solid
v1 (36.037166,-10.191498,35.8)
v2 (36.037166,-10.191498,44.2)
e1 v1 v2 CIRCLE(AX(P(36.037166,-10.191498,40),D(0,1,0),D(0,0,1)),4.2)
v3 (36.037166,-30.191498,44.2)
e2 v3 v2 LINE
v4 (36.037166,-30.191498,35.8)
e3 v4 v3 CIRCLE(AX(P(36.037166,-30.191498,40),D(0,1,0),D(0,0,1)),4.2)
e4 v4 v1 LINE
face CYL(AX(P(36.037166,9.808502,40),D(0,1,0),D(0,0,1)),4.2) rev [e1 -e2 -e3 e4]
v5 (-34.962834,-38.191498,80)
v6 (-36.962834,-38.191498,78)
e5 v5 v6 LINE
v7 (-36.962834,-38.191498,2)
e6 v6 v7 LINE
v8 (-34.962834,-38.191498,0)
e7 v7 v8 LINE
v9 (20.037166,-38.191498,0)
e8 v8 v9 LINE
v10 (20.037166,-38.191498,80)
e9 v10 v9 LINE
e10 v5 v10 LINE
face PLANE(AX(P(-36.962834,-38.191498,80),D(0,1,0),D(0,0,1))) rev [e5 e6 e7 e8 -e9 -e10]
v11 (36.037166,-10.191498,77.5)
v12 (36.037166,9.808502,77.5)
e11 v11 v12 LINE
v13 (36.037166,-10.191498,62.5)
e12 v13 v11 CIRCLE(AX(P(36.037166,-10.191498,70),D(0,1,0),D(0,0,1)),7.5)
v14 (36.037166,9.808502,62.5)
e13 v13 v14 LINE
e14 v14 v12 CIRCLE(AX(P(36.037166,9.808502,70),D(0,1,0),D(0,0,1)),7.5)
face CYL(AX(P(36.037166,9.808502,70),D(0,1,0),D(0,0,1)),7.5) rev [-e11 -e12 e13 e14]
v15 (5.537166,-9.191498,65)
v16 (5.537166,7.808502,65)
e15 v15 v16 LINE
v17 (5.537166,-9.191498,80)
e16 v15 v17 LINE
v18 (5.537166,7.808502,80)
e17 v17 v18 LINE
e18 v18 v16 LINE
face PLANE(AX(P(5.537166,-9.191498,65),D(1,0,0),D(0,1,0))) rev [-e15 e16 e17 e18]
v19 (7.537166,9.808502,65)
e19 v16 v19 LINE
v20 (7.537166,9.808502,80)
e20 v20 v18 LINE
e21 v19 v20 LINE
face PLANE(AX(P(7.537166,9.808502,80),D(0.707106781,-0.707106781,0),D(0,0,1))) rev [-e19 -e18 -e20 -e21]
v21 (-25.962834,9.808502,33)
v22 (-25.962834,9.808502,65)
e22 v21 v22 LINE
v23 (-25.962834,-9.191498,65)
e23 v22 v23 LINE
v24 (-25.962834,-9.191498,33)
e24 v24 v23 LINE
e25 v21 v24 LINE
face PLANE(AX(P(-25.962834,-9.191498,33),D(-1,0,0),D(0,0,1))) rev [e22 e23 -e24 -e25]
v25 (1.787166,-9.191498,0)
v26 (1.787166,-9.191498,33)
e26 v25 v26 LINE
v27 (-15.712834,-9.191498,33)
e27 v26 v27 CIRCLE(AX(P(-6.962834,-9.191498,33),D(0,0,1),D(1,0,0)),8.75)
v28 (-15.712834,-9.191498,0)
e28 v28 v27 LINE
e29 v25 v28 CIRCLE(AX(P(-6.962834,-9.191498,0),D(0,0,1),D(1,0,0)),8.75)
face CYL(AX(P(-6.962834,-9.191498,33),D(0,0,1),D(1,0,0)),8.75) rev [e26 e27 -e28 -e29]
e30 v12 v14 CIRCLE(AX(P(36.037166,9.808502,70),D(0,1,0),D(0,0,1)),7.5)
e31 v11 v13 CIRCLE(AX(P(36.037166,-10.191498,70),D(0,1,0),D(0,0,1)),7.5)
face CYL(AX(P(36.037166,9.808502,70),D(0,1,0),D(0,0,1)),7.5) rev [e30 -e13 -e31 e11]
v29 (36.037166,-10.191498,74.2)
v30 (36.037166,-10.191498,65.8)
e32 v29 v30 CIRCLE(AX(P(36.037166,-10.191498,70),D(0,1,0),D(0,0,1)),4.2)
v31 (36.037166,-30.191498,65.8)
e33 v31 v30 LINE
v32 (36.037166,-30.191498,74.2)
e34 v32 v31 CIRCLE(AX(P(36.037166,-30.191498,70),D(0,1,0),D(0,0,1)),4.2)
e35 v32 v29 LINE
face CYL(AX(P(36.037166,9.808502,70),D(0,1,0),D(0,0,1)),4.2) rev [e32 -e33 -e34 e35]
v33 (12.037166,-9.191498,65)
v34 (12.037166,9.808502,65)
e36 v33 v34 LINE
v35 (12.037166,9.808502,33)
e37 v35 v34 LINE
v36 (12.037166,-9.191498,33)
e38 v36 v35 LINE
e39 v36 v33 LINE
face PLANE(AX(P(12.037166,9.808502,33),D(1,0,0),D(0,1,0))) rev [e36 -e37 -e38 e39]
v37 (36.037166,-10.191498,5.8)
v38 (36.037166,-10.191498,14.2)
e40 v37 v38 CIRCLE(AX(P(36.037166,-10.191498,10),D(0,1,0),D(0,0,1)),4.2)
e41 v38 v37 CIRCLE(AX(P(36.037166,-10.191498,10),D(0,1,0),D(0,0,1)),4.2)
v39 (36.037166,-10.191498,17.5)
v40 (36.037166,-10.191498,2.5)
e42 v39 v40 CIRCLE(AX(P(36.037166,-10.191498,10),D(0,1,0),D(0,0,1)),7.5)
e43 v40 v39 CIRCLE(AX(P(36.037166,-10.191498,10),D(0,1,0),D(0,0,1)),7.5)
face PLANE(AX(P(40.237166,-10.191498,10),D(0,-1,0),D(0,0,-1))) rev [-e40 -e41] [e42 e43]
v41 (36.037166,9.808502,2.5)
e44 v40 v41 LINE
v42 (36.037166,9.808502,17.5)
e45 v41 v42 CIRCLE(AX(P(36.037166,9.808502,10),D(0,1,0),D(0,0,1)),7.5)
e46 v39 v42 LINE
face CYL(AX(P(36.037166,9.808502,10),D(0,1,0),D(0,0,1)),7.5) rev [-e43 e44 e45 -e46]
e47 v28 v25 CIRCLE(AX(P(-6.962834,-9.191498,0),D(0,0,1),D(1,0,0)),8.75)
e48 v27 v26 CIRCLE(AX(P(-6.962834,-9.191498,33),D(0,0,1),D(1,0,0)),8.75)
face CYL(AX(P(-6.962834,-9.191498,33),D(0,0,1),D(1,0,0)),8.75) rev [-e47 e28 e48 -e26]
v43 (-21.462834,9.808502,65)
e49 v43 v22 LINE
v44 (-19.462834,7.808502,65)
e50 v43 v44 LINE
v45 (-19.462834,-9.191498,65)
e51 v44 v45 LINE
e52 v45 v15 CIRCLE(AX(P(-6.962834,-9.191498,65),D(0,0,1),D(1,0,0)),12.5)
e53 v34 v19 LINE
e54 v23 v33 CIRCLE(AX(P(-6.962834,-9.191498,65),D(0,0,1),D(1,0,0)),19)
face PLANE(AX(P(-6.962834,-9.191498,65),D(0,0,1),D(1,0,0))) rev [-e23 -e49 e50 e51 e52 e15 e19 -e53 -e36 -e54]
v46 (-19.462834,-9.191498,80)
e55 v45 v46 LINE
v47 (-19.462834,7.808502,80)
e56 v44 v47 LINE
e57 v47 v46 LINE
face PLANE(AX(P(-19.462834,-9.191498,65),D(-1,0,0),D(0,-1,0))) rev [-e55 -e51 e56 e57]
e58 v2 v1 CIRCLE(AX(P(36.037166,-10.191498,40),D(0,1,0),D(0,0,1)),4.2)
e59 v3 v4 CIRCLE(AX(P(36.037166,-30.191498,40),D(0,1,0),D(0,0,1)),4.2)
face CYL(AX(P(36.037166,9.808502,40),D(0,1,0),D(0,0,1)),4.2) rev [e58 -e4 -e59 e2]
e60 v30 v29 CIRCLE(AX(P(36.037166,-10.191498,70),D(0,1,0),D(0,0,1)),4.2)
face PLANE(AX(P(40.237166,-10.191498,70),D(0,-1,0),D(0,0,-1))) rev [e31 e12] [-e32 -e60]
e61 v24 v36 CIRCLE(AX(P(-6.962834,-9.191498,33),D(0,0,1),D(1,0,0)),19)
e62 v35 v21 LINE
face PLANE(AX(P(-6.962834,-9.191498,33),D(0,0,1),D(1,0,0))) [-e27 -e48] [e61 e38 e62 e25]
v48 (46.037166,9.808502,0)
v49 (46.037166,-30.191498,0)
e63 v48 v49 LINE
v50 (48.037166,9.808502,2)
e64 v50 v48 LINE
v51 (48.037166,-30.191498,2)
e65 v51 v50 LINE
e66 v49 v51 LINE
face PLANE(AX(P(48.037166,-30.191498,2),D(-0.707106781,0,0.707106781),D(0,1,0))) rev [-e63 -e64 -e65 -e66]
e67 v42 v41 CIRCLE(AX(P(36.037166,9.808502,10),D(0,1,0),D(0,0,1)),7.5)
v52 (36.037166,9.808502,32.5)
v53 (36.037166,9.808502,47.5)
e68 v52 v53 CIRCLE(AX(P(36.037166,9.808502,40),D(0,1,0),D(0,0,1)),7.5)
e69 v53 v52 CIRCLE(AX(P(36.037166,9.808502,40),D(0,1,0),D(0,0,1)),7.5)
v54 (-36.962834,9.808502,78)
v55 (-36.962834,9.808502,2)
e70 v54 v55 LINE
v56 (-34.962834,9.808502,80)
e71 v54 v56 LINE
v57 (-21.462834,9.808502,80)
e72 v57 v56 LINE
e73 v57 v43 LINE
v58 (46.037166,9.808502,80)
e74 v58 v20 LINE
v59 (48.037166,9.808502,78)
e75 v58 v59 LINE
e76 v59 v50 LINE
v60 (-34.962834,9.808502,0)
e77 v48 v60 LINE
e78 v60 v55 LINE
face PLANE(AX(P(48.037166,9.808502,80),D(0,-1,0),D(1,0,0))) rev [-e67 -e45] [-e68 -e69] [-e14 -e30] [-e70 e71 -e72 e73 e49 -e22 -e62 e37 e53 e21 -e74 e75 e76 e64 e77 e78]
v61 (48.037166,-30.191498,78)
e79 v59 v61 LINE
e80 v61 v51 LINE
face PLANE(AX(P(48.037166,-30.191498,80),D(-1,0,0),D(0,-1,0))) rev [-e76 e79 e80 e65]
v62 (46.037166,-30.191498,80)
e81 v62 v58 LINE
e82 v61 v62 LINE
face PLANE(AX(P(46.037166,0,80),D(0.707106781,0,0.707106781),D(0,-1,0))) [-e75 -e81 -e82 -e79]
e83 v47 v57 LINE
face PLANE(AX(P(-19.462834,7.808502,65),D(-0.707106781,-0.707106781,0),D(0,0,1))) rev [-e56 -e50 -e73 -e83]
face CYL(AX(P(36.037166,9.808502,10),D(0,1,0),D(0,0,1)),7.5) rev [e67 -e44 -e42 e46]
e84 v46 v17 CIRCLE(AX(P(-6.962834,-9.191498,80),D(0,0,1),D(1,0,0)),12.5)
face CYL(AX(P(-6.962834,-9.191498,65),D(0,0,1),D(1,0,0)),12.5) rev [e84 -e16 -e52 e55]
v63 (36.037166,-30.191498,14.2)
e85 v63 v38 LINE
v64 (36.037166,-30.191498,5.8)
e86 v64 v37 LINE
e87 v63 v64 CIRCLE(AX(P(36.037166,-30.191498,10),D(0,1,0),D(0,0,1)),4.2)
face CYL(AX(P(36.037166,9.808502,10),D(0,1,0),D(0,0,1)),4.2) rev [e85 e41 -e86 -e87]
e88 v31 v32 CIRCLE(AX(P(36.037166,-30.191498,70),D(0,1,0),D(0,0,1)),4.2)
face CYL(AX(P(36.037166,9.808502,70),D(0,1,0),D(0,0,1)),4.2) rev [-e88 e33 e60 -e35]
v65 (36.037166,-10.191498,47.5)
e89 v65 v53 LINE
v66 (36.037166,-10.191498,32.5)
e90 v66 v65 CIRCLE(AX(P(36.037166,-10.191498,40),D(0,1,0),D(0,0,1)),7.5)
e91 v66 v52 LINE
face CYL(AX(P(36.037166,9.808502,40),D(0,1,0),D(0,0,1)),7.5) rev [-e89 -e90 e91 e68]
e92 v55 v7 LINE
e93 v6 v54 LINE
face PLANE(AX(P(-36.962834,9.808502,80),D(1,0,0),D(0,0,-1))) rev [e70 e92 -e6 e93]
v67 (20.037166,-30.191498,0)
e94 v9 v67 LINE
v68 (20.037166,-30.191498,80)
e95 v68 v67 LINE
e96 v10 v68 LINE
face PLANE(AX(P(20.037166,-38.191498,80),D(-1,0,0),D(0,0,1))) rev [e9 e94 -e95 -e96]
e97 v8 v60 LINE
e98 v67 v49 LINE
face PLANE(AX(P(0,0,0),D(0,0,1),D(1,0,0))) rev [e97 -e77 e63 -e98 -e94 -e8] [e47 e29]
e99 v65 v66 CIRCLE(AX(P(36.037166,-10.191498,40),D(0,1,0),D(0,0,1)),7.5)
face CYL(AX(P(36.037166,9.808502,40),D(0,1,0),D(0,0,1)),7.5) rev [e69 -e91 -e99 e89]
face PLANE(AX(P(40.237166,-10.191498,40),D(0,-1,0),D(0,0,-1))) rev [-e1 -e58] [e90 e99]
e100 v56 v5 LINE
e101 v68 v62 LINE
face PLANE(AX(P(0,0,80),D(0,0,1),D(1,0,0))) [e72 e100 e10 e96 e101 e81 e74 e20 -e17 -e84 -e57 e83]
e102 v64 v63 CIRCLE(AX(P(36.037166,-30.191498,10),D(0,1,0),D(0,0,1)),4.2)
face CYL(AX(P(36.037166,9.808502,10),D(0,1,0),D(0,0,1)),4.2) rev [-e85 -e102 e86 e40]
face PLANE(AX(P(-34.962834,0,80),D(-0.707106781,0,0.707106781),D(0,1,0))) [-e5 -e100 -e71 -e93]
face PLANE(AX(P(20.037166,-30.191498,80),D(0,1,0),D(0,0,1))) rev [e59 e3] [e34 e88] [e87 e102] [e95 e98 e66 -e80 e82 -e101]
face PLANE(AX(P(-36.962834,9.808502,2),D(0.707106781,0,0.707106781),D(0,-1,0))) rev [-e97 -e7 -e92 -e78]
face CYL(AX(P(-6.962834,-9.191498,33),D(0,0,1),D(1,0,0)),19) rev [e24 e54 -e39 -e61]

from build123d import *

# Parameters (mm, degrees)
BOSS_EXTRUDE1_DEPTH = 80
CUT_EXTRUDE1_DEPTH  = 15
CUT_EXTRUDE2_DEPTH  = 32
M20_TAPPED_HOLE1_D  = 17.5
HOLE1_D             = 8.4
HOLE1_CBORE_D       = 15
HOLE1_CBORE_DEPTH   = 20
CHAMFER1_SIZE       = 2


with BuildPart() as part:
    # Sketch2 → Boss-Extrude1 (new body)
    with BuildSketch(Plane.XY):
        Polygon((-36.962834249, 9.808501666), (-36.962834249, -38.191498334), (20.037165751, -38.191498334), (20.037165751, -30.191498334), (48.037165751, -30.191498334), (48.037165751, 9.808501666), align=None)
    extrude(amount=BOSS_EXTRUDE1_DEPTH)

    # Sketch3 → Cut-Extrude1 (cut)
    with BuildSketch(Plane.XY.offset(80)):
        with BuildLine():
            Line((-19.462834249, -9.191498334), (-19.462834249, 9.808501666))
            Line((-19.462834249, 9.808501666), (5.537165751, 9.808501666))
            Line((5.537165751, 9.808501666), (5.537165751, -9.191498334))
            ThreePointArc((5.537165751, -9.191498334), (-6.962834249, -21.691498334), (-19.462834249, -9.191498334))
        make_face()
    extrude(amount=-CUT_EXTRUDE1_DEPTH, mode=Mode.SUBTRACT)

    # Sketch4 → Cut-Extrude2 (cut)
    with BuildSketch(Plane.XY.offset(65)):
        with BuildLine():
            Line((-25.962834249, -9.191498334), (-25.962834249, 9.808501666))
            Line((-25.962834249, 9.808501666), (12.037165751, 9.808501666))
            Line((12.037165751, 9.808501666), (12.037165751, -9.191498334))
            ThreePointArc((12.037165751, -9.191498334), (-6.962834249, -28.191498334), (-25.962834249, -9.191498334))
        make_face()
    extrude(amount=-CUT_EXTRUDE2_DEPTH, mode=Mode.SUBTRACT)

    # M20 Tapped Hole1 (through all)
    with Locations(Plane.XY.offset(33)):
        with Locations((-6.962834249, -9.191498334)):
            Hole(M20_TAPPED_HOLE1_D / 2)

    # Hole1 (through all)
    with Locations(Plane(origin=(0, 9.808501666, 0), x_dir=(1, 0, 0), z_dir=(0, 1, 0))):
        with Locations((36.037165751, -10), (36.037165751, -40), (36.037165751, -70)):
            CounterBoreHole(HOLE1_D / 2, HOLE1_CBORE_D / 2, HOLE1_CBORE_DEPTH)

    # Chamfer1
    chamfer1_edges = [part.edges().sort_by_distance(p)[0] for p in [
        (-19.462834249, 9.808501666, 72.5),
        (48.037165751, -10.191498334, 80),
        (5.537165751, 9.808501666, 72.5),
        (48.037165751, -10.191498334, 0),
        (-36.962834249, -14.191498334, 0),
        (-36.962834249, -14.191498334, 80),
    ]]
    chamfer(chamfer1_edges, length=CHAMFER1_SIZE)


solid = part.part
